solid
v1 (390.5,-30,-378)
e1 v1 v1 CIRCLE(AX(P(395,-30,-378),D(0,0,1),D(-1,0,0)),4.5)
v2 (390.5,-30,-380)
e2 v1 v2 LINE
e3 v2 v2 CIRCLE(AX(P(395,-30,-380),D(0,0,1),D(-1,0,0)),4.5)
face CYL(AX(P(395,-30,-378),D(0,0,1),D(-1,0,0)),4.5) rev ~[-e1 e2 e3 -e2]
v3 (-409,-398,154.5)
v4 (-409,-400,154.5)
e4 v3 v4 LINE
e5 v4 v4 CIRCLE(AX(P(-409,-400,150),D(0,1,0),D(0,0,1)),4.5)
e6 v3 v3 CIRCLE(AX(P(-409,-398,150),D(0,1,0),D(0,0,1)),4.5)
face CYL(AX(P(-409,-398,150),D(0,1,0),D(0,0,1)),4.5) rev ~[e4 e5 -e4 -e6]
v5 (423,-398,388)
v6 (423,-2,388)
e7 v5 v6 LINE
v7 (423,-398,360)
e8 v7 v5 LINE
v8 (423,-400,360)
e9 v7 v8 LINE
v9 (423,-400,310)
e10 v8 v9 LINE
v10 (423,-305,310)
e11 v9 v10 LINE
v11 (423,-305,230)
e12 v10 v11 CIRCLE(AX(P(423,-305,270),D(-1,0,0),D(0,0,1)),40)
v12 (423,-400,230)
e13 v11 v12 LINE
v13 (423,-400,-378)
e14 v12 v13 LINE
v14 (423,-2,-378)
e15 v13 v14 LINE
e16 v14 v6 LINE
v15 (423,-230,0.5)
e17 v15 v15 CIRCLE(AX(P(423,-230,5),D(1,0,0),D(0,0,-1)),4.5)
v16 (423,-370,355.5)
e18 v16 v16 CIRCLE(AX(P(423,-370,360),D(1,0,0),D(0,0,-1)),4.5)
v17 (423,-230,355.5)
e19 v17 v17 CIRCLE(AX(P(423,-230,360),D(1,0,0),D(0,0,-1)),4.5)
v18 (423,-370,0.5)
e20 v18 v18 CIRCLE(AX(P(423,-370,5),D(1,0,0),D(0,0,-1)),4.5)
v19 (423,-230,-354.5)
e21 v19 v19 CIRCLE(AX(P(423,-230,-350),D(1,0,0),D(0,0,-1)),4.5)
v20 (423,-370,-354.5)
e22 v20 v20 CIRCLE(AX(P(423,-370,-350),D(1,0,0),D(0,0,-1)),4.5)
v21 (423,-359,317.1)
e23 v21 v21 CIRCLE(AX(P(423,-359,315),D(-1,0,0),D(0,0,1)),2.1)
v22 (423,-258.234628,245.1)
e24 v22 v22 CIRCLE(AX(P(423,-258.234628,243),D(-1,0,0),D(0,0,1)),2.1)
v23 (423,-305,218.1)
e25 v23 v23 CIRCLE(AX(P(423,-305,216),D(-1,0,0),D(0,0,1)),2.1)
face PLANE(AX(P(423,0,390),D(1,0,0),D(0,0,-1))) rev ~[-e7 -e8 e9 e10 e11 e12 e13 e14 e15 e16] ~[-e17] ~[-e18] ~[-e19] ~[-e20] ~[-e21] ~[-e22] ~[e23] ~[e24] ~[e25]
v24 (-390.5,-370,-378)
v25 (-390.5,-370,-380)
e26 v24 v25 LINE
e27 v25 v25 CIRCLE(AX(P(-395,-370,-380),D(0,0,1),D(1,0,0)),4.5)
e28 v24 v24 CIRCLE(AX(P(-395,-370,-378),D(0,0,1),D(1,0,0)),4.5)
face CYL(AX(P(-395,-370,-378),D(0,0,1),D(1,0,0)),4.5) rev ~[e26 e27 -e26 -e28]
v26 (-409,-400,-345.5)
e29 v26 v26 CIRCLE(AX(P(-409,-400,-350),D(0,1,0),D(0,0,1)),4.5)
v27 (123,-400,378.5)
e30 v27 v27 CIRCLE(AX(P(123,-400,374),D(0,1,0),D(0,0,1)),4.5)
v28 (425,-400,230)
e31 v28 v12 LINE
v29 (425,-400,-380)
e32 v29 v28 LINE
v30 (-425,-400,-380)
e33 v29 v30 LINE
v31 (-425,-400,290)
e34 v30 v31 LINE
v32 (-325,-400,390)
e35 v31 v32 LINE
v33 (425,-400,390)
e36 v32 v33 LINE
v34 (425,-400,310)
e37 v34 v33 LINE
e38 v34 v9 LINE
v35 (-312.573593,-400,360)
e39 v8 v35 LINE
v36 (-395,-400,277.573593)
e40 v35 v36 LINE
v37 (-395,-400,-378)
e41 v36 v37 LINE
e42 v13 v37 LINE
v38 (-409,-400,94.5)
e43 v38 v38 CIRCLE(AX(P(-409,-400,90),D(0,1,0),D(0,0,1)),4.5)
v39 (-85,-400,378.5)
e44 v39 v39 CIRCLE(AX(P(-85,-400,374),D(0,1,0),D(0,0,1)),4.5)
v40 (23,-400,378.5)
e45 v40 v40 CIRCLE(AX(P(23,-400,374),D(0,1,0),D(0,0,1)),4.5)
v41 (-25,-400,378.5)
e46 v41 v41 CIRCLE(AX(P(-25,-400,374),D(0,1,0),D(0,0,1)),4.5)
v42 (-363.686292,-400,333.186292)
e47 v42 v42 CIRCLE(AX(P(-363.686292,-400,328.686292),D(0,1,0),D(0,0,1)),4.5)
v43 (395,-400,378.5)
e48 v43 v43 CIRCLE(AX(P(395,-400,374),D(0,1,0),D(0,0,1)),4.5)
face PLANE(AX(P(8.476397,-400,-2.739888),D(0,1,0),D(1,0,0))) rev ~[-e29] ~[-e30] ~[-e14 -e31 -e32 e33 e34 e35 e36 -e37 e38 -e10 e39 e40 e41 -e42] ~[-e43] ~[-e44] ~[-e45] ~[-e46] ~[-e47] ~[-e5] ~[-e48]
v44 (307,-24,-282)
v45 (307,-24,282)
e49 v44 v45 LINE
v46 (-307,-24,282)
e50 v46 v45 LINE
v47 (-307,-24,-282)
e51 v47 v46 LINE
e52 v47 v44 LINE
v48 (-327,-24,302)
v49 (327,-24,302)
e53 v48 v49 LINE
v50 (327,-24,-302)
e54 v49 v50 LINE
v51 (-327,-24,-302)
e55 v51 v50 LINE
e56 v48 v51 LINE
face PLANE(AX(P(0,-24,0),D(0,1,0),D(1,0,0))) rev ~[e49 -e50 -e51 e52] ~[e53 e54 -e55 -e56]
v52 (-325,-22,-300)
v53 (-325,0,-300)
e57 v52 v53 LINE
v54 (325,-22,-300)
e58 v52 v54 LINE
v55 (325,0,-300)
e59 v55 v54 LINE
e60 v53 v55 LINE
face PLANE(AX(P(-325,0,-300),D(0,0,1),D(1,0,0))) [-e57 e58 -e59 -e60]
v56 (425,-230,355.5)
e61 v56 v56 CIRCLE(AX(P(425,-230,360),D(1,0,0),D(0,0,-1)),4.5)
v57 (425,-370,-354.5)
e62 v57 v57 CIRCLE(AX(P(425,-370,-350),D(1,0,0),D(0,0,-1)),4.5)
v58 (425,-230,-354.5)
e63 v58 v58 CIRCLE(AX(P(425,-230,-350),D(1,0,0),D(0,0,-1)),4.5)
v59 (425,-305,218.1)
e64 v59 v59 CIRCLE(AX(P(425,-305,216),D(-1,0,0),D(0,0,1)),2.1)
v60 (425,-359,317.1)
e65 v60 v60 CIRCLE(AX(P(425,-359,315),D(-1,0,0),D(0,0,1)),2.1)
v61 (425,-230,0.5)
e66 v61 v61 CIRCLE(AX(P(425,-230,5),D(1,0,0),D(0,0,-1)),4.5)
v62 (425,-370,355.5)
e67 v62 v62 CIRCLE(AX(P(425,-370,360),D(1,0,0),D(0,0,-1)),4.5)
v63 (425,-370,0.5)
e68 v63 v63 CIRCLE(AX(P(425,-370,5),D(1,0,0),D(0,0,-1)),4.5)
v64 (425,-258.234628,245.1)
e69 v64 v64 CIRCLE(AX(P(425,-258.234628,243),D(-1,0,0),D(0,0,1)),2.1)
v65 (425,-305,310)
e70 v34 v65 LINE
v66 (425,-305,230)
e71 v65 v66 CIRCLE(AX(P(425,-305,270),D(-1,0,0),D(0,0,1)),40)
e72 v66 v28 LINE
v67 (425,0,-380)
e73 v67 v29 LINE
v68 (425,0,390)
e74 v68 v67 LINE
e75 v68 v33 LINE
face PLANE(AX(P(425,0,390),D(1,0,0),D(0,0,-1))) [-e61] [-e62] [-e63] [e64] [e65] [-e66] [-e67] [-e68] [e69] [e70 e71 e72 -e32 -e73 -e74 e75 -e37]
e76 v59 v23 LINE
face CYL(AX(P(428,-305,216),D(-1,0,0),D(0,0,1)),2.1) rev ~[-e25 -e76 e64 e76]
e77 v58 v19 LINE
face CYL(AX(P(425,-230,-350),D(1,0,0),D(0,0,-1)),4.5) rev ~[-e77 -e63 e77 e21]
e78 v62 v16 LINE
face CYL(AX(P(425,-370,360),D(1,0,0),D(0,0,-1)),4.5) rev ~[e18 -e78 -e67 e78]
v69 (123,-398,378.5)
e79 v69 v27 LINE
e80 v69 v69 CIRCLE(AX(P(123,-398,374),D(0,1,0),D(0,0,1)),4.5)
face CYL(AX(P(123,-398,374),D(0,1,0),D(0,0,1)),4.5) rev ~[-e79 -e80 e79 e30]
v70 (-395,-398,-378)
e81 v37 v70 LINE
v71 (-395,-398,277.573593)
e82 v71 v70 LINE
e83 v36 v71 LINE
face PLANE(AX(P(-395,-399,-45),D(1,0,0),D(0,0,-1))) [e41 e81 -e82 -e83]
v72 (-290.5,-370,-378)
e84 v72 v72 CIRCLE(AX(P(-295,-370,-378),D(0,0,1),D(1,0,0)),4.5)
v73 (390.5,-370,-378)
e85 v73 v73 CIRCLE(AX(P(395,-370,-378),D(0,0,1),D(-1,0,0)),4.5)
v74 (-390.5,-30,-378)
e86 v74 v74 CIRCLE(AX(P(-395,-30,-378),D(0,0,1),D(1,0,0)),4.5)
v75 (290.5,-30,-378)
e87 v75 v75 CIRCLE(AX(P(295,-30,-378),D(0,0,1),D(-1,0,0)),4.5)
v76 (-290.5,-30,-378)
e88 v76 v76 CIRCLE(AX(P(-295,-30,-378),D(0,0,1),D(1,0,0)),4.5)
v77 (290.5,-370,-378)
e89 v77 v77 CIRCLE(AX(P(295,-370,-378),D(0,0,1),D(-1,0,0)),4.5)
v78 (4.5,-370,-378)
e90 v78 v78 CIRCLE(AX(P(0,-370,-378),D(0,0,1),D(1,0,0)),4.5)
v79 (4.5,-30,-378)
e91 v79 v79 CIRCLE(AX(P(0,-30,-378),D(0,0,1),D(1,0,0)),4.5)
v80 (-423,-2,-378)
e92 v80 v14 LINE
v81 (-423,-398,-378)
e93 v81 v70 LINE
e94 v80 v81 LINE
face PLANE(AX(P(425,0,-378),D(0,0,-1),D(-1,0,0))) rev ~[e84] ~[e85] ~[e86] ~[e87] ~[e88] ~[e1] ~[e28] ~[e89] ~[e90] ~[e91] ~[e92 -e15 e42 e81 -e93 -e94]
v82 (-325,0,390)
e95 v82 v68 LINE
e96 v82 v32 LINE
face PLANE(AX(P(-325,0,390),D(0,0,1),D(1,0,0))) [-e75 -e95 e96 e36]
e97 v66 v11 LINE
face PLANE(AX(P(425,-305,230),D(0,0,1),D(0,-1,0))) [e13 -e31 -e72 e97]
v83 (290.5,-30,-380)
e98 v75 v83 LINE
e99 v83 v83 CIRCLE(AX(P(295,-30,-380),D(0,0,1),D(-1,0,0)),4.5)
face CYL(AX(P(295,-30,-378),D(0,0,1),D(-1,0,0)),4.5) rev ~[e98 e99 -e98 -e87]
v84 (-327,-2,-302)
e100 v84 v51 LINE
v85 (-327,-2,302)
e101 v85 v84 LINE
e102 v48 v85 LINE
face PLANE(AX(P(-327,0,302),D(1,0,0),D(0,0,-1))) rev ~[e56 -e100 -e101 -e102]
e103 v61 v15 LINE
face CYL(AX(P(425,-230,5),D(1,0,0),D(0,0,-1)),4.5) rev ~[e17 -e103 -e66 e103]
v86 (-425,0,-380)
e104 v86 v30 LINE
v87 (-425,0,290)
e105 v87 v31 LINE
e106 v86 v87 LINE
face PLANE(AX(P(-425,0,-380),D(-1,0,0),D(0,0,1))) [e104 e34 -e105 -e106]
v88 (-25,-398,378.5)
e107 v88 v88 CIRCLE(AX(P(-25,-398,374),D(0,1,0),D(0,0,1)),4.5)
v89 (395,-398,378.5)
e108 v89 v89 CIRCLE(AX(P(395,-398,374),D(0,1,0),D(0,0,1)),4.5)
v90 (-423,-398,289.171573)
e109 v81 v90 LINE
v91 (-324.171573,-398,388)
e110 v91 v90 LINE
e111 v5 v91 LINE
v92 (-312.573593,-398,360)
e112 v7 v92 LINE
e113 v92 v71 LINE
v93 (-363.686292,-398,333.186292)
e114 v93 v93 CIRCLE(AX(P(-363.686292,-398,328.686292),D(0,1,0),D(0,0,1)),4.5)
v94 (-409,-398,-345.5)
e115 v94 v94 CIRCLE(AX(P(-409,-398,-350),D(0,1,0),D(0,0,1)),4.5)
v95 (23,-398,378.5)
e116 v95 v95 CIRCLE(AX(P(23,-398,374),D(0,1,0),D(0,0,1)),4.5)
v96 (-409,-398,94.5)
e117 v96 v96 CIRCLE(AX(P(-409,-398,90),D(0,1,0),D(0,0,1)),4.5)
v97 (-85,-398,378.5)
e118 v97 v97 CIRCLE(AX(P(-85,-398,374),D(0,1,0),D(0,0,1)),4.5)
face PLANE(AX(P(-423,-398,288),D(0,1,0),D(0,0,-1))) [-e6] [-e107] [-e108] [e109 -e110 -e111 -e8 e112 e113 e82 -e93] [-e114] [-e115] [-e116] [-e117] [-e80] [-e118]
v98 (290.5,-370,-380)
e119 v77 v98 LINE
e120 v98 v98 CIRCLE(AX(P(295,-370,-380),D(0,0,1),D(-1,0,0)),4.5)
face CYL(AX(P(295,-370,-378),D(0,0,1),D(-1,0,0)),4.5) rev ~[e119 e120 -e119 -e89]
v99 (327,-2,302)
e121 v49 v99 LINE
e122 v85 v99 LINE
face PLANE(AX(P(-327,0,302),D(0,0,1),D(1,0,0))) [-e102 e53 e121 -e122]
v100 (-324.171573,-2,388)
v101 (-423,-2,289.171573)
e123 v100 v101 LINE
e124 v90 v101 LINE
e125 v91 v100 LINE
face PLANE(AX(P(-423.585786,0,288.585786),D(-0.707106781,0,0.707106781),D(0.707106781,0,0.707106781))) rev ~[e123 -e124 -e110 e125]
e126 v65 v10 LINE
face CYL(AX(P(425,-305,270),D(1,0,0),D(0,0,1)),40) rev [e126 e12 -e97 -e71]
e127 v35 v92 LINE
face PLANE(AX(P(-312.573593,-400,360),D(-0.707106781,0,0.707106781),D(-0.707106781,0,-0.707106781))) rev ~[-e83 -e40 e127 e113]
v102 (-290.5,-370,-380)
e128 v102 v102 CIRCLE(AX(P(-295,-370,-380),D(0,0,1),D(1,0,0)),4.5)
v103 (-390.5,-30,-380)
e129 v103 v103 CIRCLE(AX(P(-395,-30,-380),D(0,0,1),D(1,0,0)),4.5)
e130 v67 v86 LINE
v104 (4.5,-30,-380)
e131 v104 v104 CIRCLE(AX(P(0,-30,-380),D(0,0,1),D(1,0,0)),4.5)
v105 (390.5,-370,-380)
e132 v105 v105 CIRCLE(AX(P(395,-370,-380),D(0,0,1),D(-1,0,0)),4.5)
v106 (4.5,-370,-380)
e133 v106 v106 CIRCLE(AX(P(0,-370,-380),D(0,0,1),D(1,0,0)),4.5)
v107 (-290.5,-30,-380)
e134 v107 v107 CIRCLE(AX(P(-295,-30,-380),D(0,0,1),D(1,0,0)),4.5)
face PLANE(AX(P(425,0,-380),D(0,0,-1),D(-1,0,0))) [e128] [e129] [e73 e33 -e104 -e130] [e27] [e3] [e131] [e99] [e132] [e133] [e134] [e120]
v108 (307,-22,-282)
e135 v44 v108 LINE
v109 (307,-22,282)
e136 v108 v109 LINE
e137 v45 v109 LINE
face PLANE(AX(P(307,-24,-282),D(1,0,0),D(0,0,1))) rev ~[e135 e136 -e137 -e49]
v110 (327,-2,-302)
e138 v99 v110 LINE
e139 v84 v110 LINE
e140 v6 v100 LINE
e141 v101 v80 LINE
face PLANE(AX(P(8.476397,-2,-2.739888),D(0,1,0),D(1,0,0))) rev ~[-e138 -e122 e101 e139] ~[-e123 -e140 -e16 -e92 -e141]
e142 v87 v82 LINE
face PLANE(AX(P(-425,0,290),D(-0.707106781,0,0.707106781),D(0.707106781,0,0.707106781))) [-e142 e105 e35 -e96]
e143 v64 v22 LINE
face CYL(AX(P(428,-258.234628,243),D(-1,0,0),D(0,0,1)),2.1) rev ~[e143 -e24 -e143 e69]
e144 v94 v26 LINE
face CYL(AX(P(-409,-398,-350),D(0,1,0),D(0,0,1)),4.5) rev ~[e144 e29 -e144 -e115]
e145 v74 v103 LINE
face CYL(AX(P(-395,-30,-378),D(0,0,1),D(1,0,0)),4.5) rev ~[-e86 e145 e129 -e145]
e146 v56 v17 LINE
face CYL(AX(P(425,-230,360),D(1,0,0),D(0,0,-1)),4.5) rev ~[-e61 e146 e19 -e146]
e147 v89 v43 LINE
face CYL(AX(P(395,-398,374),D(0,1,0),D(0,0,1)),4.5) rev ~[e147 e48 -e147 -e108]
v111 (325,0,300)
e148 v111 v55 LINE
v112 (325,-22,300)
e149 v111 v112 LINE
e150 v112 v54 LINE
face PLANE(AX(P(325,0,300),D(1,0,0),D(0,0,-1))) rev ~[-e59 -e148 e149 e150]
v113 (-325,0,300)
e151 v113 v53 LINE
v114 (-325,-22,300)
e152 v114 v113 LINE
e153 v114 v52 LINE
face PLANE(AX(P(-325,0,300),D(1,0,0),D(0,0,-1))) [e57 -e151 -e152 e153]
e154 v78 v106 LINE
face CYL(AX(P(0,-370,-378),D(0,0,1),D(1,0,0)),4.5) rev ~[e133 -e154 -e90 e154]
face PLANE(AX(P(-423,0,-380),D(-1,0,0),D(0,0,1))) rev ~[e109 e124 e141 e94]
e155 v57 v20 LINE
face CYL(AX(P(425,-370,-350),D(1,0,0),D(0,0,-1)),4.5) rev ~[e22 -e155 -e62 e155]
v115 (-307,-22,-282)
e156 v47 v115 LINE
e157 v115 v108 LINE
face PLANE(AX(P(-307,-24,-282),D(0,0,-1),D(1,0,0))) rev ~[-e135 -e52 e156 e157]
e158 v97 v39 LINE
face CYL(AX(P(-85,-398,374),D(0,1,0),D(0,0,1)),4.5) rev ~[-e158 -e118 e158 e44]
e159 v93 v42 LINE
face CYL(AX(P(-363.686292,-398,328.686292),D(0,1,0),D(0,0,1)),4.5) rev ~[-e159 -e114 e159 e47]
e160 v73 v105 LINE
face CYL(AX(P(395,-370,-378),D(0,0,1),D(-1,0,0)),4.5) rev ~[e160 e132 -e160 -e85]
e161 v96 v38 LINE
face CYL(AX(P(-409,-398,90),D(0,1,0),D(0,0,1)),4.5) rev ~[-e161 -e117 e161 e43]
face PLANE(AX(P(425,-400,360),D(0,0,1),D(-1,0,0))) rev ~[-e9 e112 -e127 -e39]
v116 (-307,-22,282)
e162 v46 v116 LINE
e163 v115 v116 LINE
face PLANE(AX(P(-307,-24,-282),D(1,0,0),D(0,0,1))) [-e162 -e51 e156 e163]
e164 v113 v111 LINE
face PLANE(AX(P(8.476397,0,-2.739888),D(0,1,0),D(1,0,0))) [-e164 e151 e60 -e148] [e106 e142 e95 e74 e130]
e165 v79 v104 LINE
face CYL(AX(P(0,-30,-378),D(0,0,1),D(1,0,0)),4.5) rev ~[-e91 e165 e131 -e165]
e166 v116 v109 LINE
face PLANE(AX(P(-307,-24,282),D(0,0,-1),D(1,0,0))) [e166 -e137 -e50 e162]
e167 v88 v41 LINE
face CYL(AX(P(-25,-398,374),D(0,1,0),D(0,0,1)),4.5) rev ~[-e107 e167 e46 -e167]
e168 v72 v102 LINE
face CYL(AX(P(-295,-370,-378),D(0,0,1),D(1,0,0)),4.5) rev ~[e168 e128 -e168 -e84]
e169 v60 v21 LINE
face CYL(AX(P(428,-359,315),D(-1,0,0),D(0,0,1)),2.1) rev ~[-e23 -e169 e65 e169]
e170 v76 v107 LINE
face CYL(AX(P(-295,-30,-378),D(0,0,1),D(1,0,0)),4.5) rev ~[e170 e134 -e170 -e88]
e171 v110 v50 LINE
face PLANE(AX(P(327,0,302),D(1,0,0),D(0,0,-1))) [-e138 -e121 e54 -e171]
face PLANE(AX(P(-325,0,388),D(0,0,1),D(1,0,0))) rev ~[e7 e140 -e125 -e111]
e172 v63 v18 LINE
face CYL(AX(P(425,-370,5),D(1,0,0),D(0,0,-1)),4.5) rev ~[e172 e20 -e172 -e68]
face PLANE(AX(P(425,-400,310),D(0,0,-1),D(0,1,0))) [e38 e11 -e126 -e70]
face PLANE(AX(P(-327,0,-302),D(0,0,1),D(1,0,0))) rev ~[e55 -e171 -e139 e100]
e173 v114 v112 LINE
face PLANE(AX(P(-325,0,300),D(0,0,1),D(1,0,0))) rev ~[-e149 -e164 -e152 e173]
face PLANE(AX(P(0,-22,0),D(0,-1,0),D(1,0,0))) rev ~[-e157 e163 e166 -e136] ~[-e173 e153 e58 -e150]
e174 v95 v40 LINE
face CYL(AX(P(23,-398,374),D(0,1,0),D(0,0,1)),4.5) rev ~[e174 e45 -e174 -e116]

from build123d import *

# Parameters (mm, degrees)
EXTRUDE_1_DEPTH        = 400
SHELL_1_T              = -2
SKETCH_3_W             = 650
SKETCH_3_H             = 600
CUT_EXTRUDE_1_DEPTH    = 2
SKETCH_4_W             = 654
SKETCH_4_H             = 604
SKETCH_4_W_2           = 650
SKETCH_4_H_2           = 600
EXTRUDE_2_DEPTH        = 24
SKETCH_5_W             = 654
SKETCH_5_H             = 604
SKETCH_5_W_2           = 614
SKETCH_5_H_2           = 564
EXTRUDE_3_DEPTH        = 2
EXTRUDE_4_DEPTH        = 2
CUT_EXTRUDE_2_DEPTH    = 2
SKETCH_10_W            = 666
SKETCH_10_H            = 2
EXTRUDE_7_DEPTH        = 28
SKETCH_12_R            = 4.5
CUT_EXTRUDE_3_DEPTH    = 10
SKETCH_13_R            = 4.5
CUT_EXTRUDE_4_DEPTH    = 10
SKETCH_14_R            = 4.5
CUT_EXTRUDE_5_DEPTH    = 10
HOLE_WIZARD_M5_1_D     = 4.2
HOLE_WIZARD_M5_1_DEPTH = 3
HOLE_WIZARD_M5_1_TIP   = 1.2618073


with BuildPart() as part:
    # 草图1 → 凸台-拉伸1 (new body)
    with BuildSketch(Plane(origin=(0, 0, 0), x_dir=(1, 0, 0), z_dir=(0, 1, 0))):
        Polygon((-425, 380), (-425, -290), (-325, -390), (425, -390), (425, 380), align=None)
    extrude(amount=-EXTRUDE_1_DEPTH)

    # 抽壳1
    shell_1_openings = [part.faces().sort_by_distance(p)[0] for p in [
        (3.015139851, -400, 2.292789325),
    ]]
    offset(amount=SHELL_1_T, openings=shell_1_openings, kind=Kind.INTERSECTION)

    # 草图3 → 切除-拉伸1 (cut)
    with BuildSketch(Plane(origin=(0, 0, 0), x_dir=(1, 0, 0), z_dir=(0, 1, 0))):
        Rectangle(SKETCH_3_W, SKETCH_3_H)
    extrude(amount=-CUT_EXTRUDE_1_DEPTH, mode=Mode.SUBTRACT)

    # 草图4 → 凸台-拉伸2 (add)
    with BuildSketch(Plane(origin=(0, 0, 0), x_dir=(1, 0, 0), z_dir=(0, 1, 0))):
        Rectangle(SKETCH_4_W, SKETCH_4_H)
        Rectangle(SKETCH_4_W_2, SKETCH_4_H_2, mode=Mode.SUBTRACT)
    extrude(amount=-EXTRUDE_2_DEPTH)

    # 草图5 → 凸台-拉伸3 (add)
    with BuildSketch(Plane.XZ.offset(24)):
        Rectangle(SKETCH_5_W, SKETCH_5_H)
        Rectangle(SKETCH_5_W_2, SKETCH_5_H_2, mode=Mode.SUBTRACT)
    extrude(amount=-EXTRUDE_3_DEPTH)

    # 草图6 → 凸台-拉伸4 (add)
    with BuildSketch(Plane.XZ.offset(400)):
        Polygon((-425, 290), (-325, 390), (425, 390), (425, 360), (-312.573593129, 360), (-403.786796564, 268.786796564), align=None)
    extrude(amount=-EXTRUDE_4_DEPTH)

    # 草图7 → 切除-拉伸2 (cut)
    with BuildSketch(Plane(origin=(425, 0, 0), x_dir=(0, 0, -1), z_dir=(1, 0, 0))):
        with BuildLine():
            Line((-310, -400), (-310, -305))
            ThreePointArc((-310, -305), (-270, -265), (-230, -305))
            Line((-230, -305), (-230, -400))
            Line((-230, -400), (-310, -400))
        make_face()
    extrude(amount=-CUT_EXTRUDE_2_DEPTH, mode=Mode.SUBTRACT)

    # 草图10 → 凸台-拉伸7 (add)
    with BuildSketch(Plane(origin=(-423, 0, 0), x_dir=(0, 0, -1), z_dir=(1, 0, 0))):
        with Locations((45, -399)):
            Rectangle(SKETCH_10_W, SKETCH_10_H)
    extrude(amount=EXTRUDE_7_DEPTH)

    # 草图12 → 切除-拉伸3 (cut)
    with BuildSketch(Plane(origin=(0, -398, 0), x_dir=(1, 0, 0), z_dir=(0, 1, 0))):
        with Locations(Location((-409, 350, 0), (0, 0, 270))):
            Circle(SKETCH_12_R)
        with Locations(Location((-363.686291501, -328.686291501, 0), (0, 0, 270))):
            Circle(SKETCH_12_R)
        with Locations(Location((-85, -374, 0), (0, 0, 270))):
            Circle(SKETCH_12_R)
        with Locations(Location((395, -374, 0), (0, 0, 270))):
            Circle(SKETCH_12_R)
        with Locations(Location((-409, -90, 0), (0, 0, 270))):
            Circle(SKETCH_12_R)
        with Locations(Location((-25, -374, 0), (0, 0, 270))):
            Circle(SKETCH_12_R)
        with Locations(Location((-409, -150, 0), (0, 0, 270))):
            Circle(SKETCH_12_R)
        with Locations(Location((23, -374, 0), (0, 0, 270))):
            Circle(SKETCH_12_R)
        with Locations(Location((123, -374, 0), (0, 0, 270))):
            Circle(SKETCH_12_R)
    extrude(amount=-CUT_EXTRUDE_3_DEPTH, mode=Mode.SUBTRACT)

    # 草图13 → 切除-拉伸4 (cut)
    with BuildSketch(Plane.XY.offset(-378)):
        with Locations((0, -30)):
            Circle(SKETCH_13_R)
        with Locations((-295, -30)):
            Circle(SKETCH_13_R)
        with Locations((0, -370)):
            Circle(SKETCH_13_R)
        with Locations((-295, -370)):
            Circle(SKETCH_13_R)
        with Locations((-395, -30)):
            Circle(SKETCH_13_R)
        with Locations((-395, -370)):
            Circle(SKETCH_13_R)
        with Locations(Location((295, -30, 0), (0, 0, 180))):
            Circle(SKETCH_13_R)
        with Locations(Location((295, -370, 0), (0, 0, 180))):
            Circle(SKETCH_13_R)
        with Locations(Location((395, -370, 0), (0, 0, 180))):
            Circle(SKETCH_13_R)
        with Locations(Location((395, -30, 0), (0, 0, 180))):
            Circle(SKETCH_13_R)
    extrude(amount=-CUT_EXTRUDE_4_DEPTH, mode=Mode.SUBTRACT)

    # 草图14 → 切除-拉伸5 (cut)
    with BuildSketch(Plane(origin=(425, 0, 0), x_dir=(0, 0, -1), z_dir=(1, 0, 0))):
        with Locations((-360, -230)):
            Circle(SKETCH_14_R)
        with Locations((-360, -370)):
            Circle(SKETCH_14_R)
        with Locations((-5, -230)):
            Circle(SKETCH_14_R)
        with Locations((-5, -370)):
            Circle(SKETCH_14_R)
        with Locations((350, -370)):
            Circle(SKETCH_14_R)
        with Locations((350, -230)):
            Circle(SKETCH_14_R)
    extrude(amount=-CUT_EXTRUDE_5_DEPTH, mode=Mode.SUBTRACT)

    # M5 螺纹孔1
    with Locations(Plane(origin=(425, 0, 0), x_dir=(0, 0, -1), z_dir=(1, 0, 0))):
        with Locations((-243, -258.234628196), (-216, -305), (-315, -359)):
            Hole(HOLE_WIZARD_M5_1_D / 2, depth=HOLE_WIZARD_M5_1_DEPTH)
            with Locations((0, 0, -(HOLE_WIZARD_M5_1_DEPTH + HOLE_WIZARD_M5_1_TIP / 2))):  # 118° drill point
                Cone(0, HOLE_WIZARD_M5_1_D / 2, HOLE_WIZARD_M5_1_TIP, mode=Mode.SUBTRACT)


solid = part.part
